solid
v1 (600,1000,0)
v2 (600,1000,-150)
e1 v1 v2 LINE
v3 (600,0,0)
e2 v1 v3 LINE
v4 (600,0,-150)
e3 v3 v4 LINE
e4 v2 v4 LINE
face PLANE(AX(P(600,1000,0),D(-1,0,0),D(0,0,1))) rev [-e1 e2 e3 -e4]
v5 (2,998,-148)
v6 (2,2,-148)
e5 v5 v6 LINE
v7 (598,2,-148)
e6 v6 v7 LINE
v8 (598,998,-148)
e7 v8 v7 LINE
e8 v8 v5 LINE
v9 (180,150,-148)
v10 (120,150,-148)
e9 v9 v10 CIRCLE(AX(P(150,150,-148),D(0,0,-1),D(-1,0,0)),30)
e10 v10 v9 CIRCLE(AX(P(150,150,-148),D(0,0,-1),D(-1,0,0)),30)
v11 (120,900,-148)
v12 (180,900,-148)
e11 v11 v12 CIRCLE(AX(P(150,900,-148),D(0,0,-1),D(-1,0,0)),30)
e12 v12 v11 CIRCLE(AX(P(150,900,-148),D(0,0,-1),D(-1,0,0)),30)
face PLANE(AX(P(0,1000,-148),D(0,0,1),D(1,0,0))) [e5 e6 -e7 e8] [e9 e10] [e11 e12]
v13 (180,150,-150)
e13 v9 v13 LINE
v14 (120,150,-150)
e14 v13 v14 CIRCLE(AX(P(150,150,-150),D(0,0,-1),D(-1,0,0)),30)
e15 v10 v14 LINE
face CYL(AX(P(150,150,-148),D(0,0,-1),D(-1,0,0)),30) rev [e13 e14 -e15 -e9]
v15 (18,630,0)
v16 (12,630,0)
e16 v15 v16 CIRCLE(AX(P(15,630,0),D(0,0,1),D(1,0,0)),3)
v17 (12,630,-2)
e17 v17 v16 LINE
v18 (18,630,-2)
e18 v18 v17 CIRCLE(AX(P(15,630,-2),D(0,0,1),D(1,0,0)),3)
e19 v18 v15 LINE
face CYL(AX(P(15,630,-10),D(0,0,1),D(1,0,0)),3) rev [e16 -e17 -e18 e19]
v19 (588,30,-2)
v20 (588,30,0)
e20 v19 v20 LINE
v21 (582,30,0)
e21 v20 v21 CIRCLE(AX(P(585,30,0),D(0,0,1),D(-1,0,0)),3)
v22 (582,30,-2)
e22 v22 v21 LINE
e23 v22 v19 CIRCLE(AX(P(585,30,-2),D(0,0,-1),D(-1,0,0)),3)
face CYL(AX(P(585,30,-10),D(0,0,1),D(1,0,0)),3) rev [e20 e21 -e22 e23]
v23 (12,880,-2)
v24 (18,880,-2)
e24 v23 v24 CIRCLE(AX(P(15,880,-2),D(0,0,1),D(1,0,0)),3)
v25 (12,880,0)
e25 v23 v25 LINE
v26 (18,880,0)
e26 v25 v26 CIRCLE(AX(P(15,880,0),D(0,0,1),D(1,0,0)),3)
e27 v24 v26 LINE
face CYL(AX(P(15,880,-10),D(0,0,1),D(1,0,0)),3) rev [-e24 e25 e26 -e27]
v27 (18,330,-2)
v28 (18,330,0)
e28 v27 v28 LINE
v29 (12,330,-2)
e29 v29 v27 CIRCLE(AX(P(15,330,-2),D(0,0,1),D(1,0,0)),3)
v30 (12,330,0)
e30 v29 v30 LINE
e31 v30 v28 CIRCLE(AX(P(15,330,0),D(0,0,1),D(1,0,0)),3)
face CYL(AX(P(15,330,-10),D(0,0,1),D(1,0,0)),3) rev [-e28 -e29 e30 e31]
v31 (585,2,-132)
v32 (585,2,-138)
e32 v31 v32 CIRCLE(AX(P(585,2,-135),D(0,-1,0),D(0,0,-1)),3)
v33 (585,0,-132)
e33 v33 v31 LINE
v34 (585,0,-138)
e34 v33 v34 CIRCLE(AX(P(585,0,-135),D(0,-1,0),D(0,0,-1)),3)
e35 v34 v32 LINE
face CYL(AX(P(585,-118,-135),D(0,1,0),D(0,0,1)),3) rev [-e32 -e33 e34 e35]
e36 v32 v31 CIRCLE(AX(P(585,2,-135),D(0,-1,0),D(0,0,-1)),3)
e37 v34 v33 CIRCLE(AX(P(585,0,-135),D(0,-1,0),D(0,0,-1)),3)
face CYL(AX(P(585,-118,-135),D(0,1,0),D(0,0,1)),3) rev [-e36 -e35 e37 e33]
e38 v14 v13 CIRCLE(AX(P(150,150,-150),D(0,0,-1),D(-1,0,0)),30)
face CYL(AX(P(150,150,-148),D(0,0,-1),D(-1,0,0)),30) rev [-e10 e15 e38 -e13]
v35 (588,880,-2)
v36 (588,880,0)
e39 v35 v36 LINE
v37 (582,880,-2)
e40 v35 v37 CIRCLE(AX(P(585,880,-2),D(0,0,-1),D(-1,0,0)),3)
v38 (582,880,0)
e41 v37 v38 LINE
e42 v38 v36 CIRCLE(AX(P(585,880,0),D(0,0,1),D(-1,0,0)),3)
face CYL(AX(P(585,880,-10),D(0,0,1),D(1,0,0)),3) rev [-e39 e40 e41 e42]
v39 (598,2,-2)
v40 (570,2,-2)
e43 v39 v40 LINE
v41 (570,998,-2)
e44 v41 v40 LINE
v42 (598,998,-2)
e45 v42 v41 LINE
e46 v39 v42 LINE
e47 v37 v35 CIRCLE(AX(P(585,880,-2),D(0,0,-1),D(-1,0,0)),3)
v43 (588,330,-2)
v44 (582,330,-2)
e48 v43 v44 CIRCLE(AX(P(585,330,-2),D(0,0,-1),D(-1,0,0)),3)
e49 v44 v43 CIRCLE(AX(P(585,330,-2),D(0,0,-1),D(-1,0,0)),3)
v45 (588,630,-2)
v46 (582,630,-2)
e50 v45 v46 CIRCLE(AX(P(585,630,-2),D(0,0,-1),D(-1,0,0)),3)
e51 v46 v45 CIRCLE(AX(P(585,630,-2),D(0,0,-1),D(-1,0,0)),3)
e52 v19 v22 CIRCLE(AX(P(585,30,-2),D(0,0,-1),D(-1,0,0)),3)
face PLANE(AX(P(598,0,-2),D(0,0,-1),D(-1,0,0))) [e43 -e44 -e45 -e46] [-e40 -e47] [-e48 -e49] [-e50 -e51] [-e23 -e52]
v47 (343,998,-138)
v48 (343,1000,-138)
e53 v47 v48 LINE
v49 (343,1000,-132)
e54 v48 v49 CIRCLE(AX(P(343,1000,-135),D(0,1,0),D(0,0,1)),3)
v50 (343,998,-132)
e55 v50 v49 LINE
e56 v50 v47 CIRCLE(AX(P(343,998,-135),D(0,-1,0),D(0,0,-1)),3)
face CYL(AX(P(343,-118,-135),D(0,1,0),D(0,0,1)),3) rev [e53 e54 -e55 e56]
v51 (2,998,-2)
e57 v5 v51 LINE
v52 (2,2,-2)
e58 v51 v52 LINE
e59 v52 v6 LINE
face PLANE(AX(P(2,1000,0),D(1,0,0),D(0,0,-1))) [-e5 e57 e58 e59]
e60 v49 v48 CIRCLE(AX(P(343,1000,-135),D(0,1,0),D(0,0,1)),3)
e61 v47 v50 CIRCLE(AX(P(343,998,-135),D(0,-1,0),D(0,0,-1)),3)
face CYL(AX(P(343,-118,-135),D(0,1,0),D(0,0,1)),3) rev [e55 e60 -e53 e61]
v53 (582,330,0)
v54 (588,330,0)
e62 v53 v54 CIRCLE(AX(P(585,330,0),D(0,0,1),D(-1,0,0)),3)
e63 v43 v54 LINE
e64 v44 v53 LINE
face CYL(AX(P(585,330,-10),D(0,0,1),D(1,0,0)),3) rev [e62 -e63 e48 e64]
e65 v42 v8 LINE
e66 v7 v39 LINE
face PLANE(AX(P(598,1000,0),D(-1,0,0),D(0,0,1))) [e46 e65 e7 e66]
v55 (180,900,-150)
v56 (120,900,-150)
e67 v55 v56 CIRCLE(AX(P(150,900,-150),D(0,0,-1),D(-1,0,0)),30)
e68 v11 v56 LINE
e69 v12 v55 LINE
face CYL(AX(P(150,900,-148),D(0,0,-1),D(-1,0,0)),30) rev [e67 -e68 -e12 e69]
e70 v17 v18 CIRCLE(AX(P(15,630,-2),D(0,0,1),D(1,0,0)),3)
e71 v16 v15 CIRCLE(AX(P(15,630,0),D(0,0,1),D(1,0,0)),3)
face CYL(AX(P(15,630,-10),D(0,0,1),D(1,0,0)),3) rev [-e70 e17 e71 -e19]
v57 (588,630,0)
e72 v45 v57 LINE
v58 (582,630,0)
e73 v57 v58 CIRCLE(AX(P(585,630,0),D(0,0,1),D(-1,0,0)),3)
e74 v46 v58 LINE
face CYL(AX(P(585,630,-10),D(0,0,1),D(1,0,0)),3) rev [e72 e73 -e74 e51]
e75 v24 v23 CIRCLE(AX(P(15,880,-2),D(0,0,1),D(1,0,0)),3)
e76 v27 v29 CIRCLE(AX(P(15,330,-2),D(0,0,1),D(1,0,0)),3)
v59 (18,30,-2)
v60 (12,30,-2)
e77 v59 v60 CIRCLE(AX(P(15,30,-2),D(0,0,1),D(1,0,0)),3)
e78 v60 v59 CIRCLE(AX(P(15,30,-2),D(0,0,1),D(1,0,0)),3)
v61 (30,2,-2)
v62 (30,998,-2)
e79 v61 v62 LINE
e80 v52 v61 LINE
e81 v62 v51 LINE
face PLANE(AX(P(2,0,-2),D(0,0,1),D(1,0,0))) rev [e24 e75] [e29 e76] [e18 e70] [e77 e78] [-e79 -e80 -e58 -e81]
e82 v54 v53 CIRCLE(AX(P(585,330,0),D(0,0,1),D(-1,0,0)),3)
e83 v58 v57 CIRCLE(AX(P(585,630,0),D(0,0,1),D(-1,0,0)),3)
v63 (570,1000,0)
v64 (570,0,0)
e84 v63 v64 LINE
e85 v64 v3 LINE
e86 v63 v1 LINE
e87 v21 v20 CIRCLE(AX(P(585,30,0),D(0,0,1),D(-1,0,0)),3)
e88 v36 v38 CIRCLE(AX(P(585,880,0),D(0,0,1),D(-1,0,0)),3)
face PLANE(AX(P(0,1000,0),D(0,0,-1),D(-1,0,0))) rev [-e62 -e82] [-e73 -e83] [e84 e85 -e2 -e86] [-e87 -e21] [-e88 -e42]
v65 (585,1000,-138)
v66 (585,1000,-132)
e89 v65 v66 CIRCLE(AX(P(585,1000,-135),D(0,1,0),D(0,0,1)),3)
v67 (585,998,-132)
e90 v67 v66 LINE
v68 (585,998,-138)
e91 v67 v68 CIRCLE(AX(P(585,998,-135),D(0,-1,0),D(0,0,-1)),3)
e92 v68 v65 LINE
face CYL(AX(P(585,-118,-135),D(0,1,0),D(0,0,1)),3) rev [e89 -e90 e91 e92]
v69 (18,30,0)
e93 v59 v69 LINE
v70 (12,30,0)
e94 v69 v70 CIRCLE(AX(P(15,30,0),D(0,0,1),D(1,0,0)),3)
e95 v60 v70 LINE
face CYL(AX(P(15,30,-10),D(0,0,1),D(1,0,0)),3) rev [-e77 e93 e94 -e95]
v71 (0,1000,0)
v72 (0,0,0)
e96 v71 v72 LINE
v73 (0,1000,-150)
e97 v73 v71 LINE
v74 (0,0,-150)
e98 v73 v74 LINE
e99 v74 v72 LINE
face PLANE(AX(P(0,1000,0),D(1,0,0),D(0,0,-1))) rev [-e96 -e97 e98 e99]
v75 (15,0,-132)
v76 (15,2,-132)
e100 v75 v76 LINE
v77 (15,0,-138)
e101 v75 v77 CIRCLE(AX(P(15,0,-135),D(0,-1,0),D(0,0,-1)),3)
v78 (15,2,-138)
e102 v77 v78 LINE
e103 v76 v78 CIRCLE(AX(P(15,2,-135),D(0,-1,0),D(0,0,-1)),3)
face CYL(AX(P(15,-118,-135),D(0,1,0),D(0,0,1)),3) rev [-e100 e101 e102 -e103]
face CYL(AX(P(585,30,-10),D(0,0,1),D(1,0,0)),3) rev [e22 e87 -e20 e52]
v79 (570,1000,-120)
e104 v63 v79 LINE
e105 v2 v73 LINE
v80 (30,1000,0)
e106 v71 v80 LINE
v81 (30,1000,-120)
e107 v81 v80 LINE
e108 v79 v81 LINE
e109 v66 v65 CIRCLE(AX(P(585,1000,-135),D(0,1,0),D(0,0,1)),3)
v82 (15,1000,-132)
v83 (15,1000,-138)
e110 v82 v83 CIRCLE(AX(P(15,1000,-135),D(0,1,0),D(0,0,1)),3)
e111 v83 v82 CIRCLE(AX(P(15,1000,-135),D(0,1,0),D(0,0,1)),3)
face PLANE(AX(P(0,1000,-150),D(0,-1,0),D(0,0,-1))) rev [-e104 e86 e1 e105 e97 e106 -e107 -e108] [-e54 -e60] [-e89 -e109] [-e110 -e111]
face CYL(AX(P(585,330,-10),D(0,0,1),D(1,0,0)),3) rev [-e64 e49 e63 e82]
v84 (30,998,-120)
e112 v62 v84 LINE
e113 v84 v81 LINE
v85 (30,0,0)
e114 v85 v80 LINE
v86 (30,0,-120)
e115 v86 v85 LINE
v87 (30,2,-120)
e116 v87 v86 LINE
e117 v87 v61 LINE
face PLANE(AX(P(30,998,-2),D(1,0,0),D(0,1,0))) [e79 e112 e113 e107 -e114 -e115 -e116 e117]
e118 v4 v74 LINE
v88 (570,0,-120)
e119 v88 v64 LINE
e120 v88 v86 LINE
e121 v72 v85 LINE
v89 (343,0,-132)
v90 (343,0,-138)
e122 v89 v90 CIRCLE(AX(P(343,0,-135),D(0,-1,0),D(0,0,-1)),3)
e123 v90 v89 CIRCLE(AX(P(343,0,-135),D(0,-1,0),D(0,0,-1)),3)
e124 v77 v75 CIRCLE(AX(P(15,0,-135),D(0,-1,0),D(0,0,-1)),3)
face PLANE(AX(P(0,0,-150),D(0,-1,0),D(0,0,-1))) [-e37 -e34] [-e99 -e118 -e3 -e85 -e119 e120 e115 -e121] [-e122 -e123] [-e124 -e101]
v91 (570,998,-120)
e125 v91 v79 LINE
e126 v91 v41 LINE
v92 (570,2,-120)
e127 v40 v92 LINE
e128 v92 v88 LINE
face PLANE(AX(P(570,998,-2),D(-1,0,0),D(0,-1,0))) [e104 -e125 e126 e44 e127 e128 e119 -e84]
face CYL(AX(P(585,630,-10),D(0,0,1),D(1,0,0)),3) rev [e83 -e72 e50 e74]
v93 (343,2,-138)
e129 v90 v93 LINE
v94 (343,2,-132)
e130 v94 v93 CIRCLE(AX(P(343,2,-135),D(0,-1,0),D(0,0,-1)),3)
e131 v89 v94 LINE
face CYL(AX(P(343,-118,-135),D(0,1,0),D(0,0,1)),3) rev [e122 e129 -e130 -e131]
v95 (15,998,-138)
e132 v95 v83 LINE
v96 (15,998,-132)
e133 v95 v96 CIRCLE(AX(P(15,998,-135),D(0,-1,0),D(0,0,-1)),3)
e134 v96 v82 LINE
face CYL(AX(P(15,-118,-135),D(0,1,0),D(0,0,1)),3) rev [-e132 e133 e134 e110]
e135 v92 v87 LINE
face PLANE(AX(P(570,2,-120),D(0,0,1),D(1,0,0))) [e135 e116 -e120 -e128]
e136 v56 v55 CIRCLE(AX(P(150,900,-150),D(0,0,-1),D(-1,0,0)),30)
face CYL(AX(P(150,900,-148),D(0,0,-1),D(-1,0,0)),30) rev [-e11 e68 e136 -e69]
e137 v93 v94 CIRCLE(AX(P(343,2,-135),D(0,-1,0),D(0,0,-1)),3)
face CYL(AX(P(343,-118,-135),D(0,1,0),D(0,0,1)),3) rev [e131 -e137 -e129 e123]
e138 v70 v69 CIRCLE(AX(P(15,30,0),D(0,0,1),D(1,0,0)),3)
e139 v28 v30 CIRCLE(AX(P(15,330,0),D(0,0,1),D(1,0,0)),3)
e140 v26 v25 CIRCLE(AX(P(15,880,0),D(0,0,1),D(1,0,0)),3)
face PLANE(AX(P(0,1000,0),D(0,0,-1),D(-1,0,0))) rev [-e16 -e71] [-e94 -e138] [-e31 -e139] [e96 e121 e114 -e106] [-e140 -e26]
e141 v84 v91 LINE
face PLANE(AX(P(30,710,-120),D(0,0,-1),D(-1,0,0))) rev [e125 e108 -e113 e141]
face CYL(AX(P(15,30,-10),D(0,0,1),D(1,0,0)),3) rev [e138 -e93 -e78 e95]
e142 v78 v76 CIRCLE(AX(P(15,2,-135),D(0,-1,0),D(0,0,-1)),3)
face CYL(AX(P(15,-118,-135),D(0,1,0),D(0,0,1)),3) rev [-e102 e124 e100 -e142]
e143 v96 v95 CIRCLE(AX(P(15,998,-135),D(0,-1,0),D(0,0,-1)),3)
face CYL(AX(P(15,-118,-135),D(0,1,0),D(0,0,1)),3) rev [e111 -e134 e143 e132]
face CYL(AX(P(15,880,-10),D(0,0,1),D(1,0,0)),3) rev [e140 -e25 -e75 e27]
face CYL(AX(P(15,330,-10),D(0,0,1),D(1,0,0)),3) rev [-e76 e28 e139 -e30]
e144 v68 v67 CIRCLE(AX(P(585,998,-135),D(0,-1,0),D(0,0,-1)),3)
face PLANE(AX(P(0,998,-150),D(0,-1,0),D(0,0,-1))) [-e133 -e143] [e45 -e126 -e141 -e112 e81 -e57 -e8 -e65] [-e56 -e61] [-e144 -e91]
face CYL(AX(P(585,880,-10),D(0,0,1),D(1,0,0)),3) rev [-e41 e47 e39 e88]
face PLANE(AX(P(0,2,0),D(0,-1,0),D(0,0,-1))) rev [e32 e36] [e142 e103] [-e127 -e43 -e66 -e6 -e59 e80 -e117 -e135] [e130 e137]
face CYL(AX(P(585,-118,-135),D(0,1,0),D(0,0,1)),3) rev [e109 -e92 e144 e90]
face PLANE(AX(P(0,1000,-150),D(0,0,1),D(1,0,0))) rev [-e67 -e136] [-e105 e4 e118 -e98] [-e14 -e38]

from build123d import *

# Parameters (mm, degrees)
SKETCH_1_W          = 600
SKETCH_1_H          = 150
EXTRUDE_1_DEPTH     = 1000
SHELL_1_T           = -2
SKETCH_3_W          = 596
SKETCH_3_H          = 148
CUT_EXTRUDE_1_DEPTH = 400
SKETCH_4_W          = 28
SKETCH_4_H          = 998
EXTRUDE_2_DEPTH     = 2
SKETCH_5_R          = 30
CUT_EXTRUDE_2_DEPTH = 2
SKETCH_6_W          = 540
SKETCH_6_H          = 120
CUT_EXTRUDE_3_DEPTH = 290
EXTRUDE_3_DEPTH     = 2
SKETCH_8_R          = 3
CUT_EXTRUDE_4_DEPTH = 1118
SKETCH_9_R          = 3
CUT_EXTRUDE_5_DEPTH = 10


with BuildPart() as part:
    # 草图1 → 凸台-拉伸1 (new body)
    with BuildSketch(Plane(origin=(0, 0, 0), x_dir=(1, 0, 0), z_dir=(0, 1, 0))):
        with Locations((300, 75)):
            Rectangle(SKETCH_1_W, SKETCH_1_H)
    extrude(amount=EXTRUDE_1_DEPTH)

    # 抽壳1
    shell_1_openings = [part.faces().sort_by_distance(p)[0] for p in [
        (300, 500, 0),
    ]]
    offset(amount=SHELL_1_T, openings=shell_1_openings, kind=Kind.INTERSECTION)

    # 草图3 → 切除-拉伸1 (cut)
    with BuildSketch(Plane.XZ):
        with Locations((300, -74)):
            Rectangle(SKETCH_3_W, SKETCH_3_H)
    extrude(amount=-CUT_EXTRUDE_1_DEPTH, mode=Mode.SUBTRACT)

    # 草图4 → 凸台-拉伸2 (add)
    with BuildSketch(Plane.XY):
        with Locations((16, 499)):
            Rectangle(SKETCH_4_W, SKETCH_4_H)
        with Locations((584, 499)):
            Rectangle(SKETCH_4_W, SKETCH_4_H)
    extrude(amount=-EXTRUDE_2_DEPTH)

    # 草图5 → 切除-拉伸2 (cut)
    with BuildSketch(Plane(origin=(0, 0, -150), x_dir=(-1, 0, 0), z_dir=(0, 0, -1))):
        with Locations((-150, 150)):
            Circle(SKETCH_5_R)
        with Locations((-150, 900)):
            Circle(SKETCH_5_R)
    extrude(amount=-CUT_EXTRUDE_2_DEPTH, mode=Mode.SUBTRACT)

    # 草图6 → 切除-拉伸3 (cut)
    with BuildSketch(Plane(origin=(0, 1000, 0), x_dir=(1, 0, 0), z_dir=(0, 1, 0))):
        with Locations((300, 60)):
            Rectangle(SKETCH_6_W, SKETCH_6_H)
    extrude(amount=-CUT_EXTRUDE_3_DEPTH, mode=Mode.SUBTRACT)

    # 草图7 → 凸台-拉伸3 (add)
    with BuildSketch(Plane.XZ):
        Polygon((0, 0), (0, -150), (600, -150), (600, 0), (570, 0), (570, -120), (30, -120), (30, 0), align=None)
    extrude(amount=-EXTRUDE_3_DEPTH)

    # 草图8 → 切除-拉伸4 (cut)
    with BuildSketch(Plane(origin=(0, 1000, 0), x_dir=(1, 0, 0), z_dir=(0, 1, 0))):
        with Locations(Location((15, 135, 0), (0, 0, 90))):
            Circle(SKETCH_8_R)
        with Locations(Location((343, 135, 0), (0, 0, 90))):
            Circle(SKETCH_8_R)
        with Locations(Location((585, 135, 0), (0, 0, 90))):
            Circle(SKETCH_8_R)
    extrude(amount=-CUT_EXTRUDE_4_DEPTH, mode=Mode.SUBTRACT)

    # 草图9 → 切除-拉伸5 (cut)
    with BuildSketch(Plane.XY):
        with Locations((15, 880)):
            Circle(SKETCH_9_R)
        with Locations((15, 30)):
            Circle(SKETCH_9_R)
        with Locations(Location((585, 880, 0), (0, 0, 180))):
            Circle(SKETCH_9_R)
        with Locations((15, 330)):
            Circle(SKETCH_9_R)
        with Locations(Location((585, 630, 0), (0, 0, 180))):
            Circle(SKETCH_9_R)
        with Locations((15, 630)):
            Circle(SKETCH_9_R)
        with Locations(Location((585, 330, 0), (0, 0, 180))):
            Circle(SKETCH_9_R)
        with Locations(Location((585, 30, 0), (0, 0, 180))):
            Circle(SKETCH_9_R)
    extrude(amount=-CUT_EXTRUDE_5_DEPTH, mode=Mode.SUBTRACT)


solid = part.part
